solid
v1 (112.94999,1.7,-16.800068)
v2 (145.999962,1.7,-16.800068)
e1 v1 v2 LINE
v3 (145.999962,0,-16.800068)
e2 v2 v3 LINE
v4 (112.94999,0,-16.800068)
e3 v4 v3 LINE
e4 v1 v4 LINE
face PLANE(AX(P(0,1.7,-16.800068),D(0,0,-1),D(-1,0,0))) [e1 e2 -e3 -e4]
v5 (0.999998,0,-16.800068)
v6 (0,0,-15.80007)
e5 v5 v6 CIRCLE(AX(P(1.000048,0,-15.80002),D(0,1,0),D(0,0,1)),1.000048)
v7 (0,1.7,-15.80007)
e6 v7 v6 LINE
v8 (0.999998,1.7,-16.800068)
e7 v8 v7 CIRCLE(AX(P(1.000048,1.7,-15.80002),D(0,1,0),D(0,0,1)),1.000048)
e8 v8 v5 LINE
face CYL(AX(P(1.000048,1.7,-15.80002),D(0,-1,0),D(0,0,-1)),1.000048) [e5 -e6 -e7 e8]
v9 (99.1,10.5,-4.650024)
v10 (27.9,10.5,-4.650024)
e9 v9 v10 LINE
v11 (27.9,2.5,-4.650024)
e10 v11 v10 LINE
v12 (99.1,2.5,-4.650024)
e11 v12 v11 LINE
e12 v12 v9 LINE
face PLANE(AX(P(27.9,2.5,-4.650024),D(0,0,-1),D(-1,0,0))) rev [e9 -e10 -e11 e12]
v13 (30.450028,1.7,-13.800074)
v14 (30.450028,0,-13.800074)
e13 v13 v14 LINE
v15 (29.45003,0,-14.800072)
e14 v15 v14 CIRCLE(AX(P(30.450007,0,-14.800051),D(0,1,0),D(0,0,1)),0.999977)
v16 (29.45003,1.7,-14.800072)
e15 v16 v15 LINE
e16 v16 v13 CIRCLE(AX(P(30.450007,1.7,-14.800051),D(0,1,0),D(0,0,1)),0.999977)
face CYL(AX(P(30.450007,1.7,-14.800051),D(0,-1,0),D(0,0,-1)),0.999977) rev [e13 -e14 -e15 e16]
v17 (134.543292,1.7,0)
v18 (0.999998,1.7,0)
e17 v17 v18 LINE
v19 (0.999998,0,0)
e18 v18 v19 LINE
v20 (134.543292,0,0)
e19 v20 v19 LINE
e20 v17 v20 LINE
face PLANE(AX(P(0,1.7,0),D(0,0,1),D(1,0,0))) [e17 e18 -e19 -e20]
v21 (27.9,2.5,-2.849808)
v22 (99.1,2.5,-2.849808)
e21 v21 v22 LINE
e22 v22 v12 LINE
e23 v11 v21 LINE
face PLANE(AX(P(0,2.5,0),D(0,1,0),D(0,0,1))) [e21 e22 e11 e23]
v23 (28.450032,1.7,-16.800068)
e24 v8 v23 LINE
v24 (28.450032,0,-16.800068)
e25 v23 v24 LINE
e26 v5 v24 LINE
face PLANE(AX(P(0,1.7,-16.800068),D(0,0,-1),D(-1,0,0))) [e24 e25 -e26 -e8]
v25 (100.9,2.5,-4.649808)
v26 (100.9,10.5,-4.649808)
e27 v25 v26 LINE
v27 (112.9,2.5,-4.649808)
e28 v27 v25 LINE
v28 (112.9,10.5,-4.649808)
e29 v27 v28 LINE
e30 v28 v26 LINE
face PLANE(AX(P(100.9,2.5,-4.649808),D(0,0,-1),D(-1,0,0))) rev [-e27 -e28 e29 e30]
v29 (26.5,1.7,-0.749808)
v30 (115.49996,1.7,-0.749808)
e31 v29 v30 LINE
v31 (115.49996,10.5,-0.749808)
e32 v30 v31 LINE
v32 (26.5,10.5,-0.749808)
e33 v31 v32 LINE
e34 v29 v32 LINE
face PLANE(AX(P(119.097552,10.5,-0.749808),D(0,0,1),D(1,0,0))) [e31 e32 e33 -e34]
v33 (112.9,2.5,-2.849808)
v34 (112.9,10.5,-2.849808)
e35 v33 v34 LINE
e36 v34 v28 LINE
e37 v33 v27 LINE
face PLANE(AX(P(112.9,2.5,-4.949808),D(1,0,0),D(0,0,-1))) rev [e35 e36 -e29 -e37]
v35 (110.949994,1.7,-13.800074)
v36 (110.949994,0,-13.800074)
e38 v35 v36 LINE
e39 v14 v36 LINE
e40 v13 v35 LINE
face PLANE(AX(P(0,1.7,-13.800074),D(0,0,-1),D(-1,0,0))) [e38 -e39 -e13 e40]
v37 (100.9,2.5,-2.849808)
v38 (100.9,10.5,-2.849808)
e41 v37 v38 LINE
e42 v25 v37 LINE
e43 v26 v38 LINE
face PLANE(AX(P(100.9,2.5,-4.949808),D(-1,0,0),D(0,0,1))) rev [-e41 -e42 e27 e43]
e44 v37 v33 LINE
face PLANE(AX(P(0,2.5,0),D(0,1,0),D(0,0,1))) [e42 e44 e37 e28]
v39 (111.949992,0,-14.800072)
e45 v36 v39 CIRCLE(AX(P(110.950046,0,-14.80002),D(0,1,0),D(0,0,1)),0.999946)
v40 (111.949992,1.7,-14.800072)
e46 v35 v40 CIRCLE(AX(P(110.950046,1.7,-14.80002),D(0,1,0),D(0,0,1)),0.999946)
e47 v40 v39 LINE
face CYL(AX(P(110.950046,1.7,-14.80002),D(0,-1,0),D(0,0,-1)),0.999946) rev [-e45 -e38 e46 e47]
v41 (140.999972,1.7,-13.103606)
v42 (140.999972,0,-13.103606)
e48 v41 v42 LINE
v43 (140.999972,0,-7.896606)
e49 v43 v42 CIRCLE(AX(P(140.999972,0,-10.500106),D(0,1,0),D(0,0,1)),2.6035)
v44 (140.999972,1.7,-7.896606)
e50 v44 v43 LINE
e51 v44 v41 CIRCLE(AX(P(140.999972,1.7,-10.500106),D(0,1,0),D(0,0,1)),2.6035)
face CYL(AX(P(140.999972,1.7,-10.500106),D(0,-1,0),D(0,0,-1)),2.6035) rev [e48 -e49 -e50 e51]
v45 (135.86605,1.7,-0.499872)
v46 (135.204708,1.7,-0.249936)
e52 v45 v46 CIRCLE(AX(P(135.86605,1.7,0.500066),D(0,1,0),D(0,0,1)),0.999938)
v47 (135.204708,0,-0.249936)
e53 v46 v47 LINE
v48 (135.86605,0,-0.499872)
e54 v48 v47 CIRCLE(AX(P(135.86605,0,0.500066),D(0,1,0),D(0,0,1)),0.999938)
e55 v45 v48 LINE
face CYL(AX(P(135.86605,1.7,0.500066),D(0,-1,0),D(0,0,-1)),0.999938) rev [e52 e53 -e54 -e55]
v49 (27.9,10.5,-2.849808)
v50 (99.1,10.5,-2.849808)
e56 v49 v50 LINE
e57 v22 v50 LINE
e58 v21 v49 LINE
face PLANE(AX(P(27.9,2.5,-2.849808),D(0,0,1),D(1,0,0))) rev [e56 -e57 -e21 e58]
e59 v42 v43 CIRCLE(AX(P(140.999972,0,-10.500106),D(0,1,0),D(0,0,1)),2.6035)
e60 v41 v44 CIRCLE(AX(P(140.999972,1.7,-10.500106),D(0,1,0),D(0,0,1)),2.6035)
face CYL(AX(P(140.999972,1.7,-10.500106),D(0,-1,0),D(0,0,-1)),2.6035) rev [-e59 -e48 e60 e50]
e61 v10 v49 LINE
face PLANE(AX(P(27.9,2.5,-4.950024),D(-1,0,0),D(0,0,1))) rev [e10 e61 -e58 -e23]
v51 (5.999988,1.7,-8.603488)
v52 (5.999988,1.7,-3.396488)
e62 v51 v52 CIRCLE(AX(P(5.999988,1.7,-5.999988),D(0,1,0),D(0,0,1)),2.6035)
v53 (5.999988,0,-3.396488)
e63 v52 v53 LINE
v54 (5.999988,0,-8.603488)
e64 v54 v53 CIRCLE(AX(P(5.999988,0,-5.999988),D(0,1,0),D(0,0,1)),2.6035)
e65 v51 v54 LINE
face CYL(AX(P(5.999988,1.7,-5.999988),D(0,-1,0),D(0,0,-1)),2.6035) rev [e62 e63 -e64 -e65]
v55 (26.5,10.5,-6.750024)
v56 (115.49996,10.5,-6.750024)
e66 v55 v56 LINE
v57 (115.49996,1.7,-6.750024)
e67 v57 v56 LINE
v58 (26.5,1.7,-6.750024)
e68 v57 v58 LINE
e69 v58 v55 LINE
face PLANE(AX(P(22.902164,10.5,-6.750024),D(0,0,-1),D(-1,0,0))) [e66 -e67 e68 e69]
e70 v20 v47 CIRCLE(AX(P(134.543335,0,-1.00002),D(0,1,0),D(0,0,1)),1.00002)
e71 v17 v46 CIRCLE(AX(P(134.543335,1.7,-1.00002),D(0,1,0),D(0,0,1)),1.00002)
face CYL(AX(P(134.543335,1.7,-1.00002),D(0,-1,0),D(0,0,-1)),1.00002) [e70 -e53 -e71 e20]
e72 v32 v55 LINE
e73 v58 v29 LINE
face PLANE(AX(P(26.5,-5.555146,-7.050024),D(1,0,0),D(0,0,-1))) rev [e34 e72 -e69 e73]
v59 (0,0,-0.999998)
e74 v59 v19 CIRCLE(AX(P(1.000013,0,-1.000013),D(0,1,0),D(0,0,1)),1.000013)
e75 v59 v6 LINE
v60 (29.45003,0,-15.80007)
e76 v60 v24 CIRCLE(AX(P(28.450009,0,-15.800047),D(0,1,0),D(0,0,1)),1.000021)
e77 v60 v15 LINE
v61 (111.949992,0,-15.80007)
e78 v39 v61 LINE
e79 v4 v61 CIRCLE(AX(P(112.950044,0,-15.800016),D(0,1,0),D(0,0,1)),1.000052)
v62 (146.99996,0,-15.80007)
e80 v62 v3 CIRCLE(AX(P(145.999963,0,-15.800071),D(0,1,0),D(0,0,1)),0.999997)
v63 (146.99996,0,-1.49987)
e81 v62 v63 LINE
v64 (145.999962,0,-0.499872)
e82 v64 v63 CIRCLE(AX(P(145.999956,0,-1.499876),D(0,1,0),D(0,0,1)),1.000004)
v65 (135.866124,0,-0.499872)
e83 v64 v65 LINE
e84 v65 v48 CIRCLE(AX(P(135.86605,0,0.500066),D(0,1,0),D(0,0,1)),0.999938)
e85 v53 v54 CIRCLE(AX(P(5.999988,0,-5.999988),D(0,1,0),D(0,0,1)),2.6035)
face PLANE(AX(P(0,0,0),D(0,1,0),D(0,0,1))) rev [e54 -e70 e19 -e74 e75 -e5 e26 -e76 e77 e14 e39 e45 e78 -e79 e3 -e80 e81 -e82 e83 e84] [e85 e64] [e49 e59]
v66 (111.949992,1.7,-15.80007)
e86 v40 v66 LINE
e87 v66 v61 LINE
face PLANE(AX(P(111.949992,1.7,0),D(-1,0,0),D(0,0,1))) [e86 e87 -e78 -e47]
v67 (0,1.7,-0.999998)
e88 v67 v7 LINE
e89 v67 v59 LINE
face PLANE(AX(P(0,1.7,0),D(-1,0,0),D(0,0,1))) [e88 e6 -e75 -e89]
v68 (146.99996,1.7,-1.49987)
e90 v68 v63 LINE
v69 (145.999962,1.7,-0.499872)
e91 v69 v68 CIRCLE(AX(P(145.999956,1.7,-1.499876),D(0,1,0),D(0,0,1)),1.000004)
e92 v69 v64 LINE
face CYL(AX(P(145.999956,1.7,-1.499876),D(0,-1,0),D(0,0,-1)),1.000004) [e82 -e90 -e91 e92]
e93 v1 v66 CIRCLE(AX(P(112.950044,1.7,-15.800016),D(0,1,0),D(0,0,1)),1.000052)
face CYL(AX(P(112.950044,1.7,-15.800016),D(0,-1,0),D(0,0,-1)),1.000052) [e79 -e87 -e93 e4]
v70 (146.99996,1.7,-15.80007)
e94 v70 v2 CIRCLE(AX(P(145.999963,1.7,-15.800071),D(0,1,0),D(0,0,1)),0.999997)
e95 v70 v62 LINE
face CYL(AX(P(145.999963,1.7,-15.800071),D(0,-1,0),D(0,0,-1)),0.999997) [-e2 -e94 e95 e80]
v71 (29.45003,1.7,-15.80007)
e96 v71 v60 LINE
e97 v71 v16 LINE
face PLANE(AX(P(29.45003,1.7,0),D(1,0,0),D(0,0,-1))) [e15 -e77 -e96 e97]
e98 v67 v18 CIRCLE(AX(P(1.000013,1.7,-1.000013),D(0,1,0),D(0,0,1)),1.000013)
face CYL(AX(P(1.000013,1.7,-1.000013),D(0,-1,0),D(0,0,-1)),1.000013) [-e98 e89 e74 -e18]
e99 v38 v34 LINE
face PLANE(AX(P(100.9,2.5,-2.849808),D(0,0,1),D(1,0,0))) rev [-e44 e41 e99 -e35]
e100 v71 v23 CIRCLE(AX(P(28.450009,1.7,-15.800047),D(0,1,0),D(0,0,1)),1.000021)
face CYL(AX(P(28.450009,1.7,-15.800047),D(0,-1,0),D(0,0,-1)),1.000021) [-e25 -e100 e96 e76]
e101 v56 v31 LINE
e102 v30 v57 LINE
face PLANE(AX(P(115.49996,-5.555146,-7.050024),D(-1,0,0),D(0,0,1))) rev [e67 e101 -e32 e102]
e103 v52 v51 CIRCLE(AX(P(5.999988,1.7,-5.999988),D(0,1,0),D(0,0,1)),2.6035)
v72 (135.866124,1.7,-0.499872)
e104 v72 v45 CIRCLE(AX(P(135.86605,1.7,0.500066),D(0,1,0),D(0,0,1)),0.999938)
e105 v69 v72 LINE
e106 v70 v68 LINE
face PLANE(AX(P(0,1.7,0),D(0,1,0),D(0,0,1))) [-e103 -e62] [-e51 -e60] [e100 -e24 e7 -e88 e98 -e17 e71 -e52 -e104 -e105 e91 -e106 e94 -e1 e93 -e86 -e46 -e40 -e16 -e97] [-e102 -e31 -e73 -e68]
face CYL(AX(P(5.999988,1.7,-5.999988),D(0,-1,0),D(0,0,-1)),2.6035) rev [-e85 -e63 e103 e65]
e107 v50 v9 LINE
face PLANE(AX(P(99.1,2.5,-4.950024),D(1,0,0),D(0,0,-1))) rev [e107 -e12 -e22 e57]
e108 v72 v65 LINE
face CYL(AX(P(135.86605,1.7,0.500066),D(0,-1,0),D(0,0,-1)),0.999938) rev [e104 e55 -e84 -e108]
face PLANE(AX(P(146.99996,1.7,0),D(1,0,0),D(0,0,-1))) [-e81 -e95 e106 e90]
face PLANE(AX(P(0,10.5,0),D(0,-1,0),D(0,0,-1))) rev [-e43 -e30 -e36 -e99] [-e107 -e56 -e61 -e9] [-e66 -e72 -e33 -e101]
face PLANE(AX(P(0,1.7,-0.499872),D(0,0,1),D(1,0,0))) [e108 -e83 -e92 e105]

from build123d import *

# Parameters (mm, degrees)
SKETCH_2_4_R        = 2.6035
SKETCH_2_4_W        = 96.195388
SKETCH_2_4_H        = 6.300216
BOSS_EXTRUDE2_DEPTH = 1.7
SKETCH_2_4_2_W      = 96.195388
SKETCH_2_4_2_H      = 6.300216
BOSS_EXTRUDE3_DEPTH = 10.5
SKETCH4_W           = 3.597592
SKETCH4_H           = 6.300216
SKETCH4_W_2         = 3.597836
CUT_EXTRUDE1_DEPTH  = 8.8
SKETCH3_W           = 71.2
SKETCH3_H           = 2.100216
SKETCH3_W_2         = 12
SKETCH3_H_2         = 2.1
CUT_EXTRUDE2_DEPTH  = 8
MOVE_FACE1_BY       = 0.3
MOVE_FACE1_2_BY     = 0.3
MOVE_FACE1_3_BY     = 0.3


with BuildPart() as part:
    # Sketch 2_4 → Boss-Extrude2 (new body)
    # profile 1 of 2: a face of its own
    with BuildSketch(Plane(origin=(0, 0, 0), x_dir=(1, 0, 0), z_dir=(0, 1, 0))):
        with BuildLine():
            Line((134.543292, 0), (0.999998, 0))
            ThreePointArc((0.999998, 0), (0.292896914, 0.292896914), (0, 0.999998))
            Line((0, 0.999998), (0, 15.80007))
            ThreePointArc((0, 15.80007), (0.292907414, 16.507160586), (0.999998, 16.800068))
            Line((0.999998, 16.800068), (28.450032, 16.800068))
            ThreePointArc((28.450032, 16.800068), (29.157130586, 16.507168586), (29.45003, 15.80007))
            Line((29.45003, 15.80007), (29.45003, 14.800072))
            ThreePointArc((29.45003, 14.800072), (29.742916414, 14.092960414), (30.450028, 13.800074))
            Line((30.450028, 13.800074), (110.949994, 13.800074))
            ThreePointArc((110.949994, 13.800074), (111.657114586, 14.092951414), (111.949992, 14.800072))
            Line((111.949992, 14.800072), (111.949992, 15.80007))
            ThreePointArc((111.949992, 15.80007), (112.242900414, 16.507159586), (112.94999, 16.800068))
            Line((112.94999, 16.800068), (145.999962, 16.800068))
            ThreePointArc((145.999962, 16.800068), (146.707067586, 16.507175586), (146.99996, 15.80007))
            Line((146.99996, 15.80007), (146.99996, 1.49987))
            ThreePointArc((146.99996, 1.49987), (146.707065586, 0.792766414), (145.999962, 0.499872))
            Line((145.999962, 0.499872), (135.866124, 0.499872))
            ThreePointArc((135.866124, 0.499872), (135.512587346, 0.435316415), (135.204708, 0.249936))
            ThreePointArc((135.204708, 0.249936), (134.896826655, 0.064560877), (134.543292, 0))
        make_face()
        with Locations(Location((140.999972, 10.500106, 0), (0, 0, 270))):
            Circle(SKETCH_2_4_R, mode=Mode.SUBTRACT)
        with Locations(Location((5.999988, 5.999988, 0), (0, 0, 270))):
            Circle(SKETCH_2_4_R, mode=Mode.SUBTRACT)
        with Locations((70.999858, 3.899916)):
            Rectangle(SKETCH_2_4_W, SKETCH_2_4_H, mode=Mode.SUBTRACT)
    # profile 2 of 2: a face of its own
    with BuildSketch(Plane(origin=(0, 0, 0), x_dir=(1, 0, 0), z_dir=(0, 1, 0))):
        with Locations((70.999858, 3.899916)):
            Rectangle(SKETCH_2_4_W, SKETCH_2_4_H)
    extrude(amount=BOSS_EXTRUDE2_DEPTH)

    # Sketch 2_4 2 → Boss-Extrude3 (add)
    with BuildSketch(Plane(origin=(0, 0, 0), x_dir=(1, 0, 0), z_dir=(0, 1, 0))):
        with Locations((70.999858, 3.899916)):
            Rectangle(SKETCH_2_4_2_W, SKETCH_2_4_2_H)
    extrude(amount=BOSS_EXTRUDE3_DEPTH)

    # Sketch4 → Cut-Extrude1 (cut)
    with BuildSketch(Plane(origin=(0, 10.5, 0), x_dir=(1, 0, 0), z_dir=(0, 1, 0))):
        with Locations((117.298756, 3.899916)):
            Rectangle(SKETCH4_W, SKETCH4_H)
        with Locations((24.701082, 3.899916)):
            Rectangle(SKETCH4_W_2, SKETCH4_H)
    extrude(amount=-CUT_EXTRUDE1_DEPTH, mode=Mode.SUBTRACT)

    # Sketch3 → Cut-Extrude2 (cut)
    with BuildSketch(Plane(origin=(0, 10.5, 0), x_dir=(1, 0, 0), z_dir=(0, 1, 0))):
        with Locations((63.5, 3.899916)):
            Rectangle(SKETCH3_W, SKETCH3_H)
        with Locations((106.9, 3.899808)):
            Rectangle(SKETCH3_W_2, SKETCH3_H_2)
    extrude(amount=-CUT_EXTRUDE2_DEPTH, mode=Mode.SUBTRACT)

    # Move Face1: a face moved outward by 0.3
    extrude(part.faces().sort_by_distance((63.5, 6.5, -4.950024))[0], amount=MOVE_FACE1_BY, dir=(0, 0, 1))

    # Move Face1 2: a face moved inward by 0.3
    extrude(part.faces().sort_by_distance((70.99998, 6.1, -7.050024))[0], amount=MOVE_FACE1_2_BY, dir=(0, 0, 1), mode=Mode.SUBTRACT)

    # Move Face1 3: a face moved outward by 0.3
    extrude(part.faces().sort_by_distance((106.9, 6.5, -4.949808))[0], amount=MOVE_FACE1_3_BY, dir=(0, 0, 1))


solid = part.part
